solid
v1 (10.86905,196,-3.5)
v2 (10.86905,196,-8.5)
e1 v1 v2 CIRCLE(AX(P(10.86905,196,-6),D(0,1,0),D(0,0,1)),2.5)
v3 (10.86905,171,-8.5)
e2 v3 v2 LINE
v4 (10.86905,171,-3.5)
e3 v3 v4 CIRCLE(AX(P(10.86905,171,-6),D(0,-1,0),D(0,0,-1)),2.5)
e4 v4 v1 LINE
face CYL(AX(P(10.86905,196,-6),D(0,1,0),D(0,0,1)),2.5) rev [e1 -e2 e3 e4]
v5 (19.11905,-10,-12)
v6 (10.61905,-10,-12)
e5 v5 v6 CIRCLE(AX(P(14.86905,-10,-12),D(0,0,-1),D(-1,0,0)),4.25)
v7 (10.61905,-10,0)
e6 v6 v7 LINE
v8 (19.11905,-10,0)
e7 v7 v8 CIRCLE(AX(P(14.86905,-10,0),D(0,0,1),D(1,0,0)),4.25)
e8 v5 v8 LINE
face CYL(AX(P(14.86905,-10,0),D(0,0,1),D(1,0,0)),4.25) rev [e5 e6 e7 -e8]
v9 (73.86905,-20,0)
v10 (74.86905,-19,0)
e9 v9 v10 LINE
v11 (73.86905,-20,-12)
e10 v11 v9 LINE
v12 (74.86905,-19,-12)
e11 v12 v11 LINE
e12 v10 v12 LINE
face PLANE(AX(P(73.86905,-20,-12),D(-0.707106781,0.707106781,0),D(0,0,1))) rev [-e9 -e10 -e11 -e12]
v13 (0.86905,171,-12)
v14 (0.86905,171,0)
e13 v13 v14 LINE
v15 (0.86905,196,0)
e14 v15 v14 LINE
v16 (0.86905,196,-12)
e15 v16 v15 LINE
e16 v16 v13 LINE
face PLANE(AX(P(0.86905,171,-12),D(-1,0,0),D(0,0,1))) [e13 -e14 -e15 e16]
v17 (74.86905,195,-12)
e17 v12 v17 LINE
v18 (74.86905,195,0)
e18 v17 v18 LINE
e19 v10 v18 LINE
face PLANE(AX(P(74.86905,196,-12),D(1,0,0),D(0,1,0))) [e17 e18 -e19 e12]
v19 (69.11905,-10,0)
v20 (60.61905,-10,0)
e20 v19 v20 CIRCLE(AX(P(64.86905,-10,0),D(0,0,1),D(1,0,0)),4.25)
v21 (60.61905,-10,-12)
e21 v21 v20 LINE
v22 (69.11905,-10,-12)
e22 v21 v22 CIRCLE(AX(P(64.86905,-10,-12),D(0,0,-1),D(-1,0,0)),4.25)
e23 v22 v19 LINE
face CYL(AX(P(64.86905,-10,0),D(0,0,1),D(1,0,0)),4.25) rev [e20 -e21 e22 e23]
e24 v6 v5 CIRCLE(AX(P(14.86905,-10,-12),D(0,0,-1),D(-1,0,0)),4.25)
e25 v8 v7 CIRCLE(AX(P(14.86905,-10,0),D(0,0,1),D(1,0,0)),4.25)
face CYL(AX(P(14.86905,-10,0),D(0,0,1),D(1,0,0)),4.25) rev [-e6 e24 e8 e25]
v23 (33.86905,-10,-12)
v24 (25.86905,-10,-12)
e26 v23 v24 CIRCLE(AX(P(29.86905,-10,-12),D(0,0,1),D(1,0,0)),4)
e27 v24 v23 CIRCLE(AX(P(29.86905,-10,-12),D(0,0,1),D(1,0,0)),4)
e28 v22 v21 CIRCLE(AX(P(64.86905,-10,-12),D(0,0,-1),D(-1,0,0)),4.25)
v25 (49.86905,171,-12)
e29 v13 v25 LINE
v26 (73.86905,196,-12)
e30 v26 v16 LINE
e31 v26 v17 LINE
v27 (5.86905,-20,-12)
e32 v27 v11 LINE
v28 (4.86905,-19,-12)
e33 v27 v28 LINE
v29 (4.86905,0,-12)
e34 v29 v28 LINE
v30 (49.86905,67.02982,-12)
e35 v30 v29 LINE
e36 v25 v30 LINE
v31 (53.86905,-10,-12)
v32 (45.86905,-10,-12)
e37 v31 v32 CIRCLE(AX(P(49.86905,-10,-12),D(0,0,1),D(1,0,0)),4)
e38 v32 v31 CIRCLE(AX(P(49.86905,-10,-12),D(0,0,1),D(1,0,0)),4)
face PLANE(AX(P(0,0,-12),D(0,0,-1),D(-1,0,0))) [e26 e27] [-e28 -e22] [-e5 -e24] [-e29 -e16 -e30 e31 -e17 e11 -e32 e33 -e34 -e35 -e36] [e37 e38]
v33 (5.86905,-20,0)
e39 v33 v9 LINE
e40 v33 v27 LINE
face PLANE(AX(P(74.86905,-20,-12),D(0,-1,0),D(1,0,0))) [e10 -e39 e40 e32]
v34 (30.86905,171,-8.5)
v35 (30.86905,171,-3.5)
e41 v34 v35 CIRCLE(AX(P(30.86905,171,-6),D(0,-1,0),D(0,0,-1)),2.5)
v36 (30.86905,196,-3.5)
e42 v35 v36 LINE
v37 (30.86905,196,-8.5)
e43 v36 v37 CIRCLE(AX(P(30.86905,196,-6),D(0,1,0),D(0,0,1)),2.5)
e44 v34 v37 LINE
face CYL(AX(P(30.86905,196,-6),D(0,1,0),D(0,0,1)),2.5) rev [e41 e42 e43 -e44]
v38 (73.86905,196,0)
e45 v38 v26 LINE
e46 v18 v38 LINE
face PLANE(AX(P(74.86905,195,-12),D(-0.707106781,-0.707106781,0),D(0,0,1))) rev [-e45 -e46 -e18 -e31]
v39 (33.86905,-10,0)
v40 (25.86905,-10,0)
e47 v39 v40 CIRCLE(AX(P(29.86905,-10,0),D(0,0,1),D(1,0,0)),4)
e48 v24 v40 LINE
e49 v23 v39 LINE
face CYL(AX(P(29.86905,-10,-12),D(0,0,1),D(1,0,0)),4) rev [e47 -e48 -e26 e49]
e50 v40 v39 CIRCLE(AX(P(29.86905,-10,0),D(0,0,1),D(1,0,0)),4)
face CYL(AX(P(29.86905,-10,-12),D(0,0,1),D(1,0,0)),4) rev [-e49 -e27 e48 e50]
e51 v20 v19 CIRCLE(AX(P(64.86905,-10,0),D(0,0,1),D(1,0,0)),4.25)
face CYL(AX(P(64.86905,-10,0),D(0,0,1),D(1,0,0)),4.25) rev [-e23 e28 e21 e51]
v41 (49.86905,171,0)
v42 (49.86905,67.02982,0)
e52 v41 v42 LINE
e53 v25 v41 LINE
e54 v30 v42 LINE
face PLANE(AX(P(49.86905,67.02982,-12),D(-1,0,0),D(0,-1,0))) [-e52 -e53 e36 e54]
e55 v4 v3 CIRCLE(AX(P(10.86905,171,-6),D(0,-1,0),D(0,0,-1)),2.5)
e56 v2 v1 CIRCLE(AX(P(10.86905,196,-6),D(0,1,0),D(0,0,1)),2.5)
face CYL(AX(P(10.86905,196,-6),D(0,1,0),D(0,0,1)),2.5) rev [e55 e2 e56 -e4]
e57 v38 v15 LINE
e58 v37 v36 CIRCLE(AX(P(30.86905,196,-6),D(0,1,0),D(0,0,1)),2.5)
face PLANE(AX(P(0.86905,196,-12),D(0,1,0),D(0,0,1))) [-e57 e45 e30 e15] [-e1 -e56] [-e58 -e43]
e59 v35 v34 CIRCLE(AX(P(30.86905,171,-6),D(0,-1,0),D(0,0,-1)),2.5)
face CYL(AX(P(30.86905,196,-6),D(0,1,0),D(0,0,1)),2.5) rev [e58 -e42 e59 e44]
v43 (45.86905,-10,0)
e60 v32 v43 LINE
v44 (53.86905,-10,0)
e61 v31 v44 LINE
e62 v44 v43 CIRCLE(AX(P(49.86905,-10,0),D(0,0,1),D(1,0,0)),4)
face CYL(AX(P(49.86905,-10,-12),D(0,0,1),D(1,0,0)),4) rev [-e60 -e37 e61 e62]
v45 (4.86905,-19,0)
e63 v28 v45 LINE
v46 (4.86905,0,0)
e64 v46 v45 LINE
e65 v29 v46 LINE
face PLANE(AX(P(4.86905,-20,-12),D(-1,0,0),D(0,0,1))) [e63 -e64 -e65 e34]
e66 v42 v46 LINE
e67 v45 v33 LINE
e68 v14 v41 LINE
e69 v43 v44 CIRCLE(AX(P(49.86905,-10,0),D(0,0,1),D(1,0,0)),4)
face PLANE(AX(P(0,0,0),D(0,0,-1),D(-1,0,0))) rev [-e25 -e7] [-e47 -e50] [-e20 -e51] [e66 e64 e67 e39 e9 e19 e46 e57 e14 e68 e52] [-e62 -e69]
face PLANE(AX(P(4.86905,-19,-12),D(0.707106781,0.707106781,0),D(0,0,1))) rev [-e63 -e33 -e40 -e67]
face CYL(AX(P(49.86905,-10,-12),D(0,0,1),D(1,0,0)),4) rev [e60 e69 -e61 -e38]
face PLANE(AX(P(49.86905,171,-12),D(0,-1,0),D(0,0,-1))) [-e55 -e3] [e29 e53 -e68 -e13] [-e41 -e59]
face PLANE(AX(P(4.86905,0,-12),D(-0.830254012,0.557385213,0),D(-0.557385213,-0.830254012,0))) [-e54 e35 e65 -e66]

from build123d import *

# Parameters (mm, degrees)
EXTRUDE_1_DEPTH             = 12
HOLE_WIZARD_8_5_8_5_1_D     = 8.5
HOLE_WIZARD_8_5_8_5_1_DEPTH = 15.61
HOLE_WIZARD_8_5_8_5_1_TIP   = 2.453738644
SKETCH_5_R                  = 4
CUT_EXTRUDE_1_DEPTH         = 12
HOLE_WIZARD_M6_1_D          = 5
HOLE_WIZARD_M6_1_DEPTH      = 25
CHAMFER_1_SIZE              = 1
CHAMFER_2_SIZE              = 1


with BuildPart() as part:
    # 草图1 → 凸台-拉伸1 (new body)
    with BuildSketch(Plane.XY):
        Polygon((74.869050236, -20), (4.869050236, -20), (4.869050236, 0), (49.869050236, 67.029820029), (49.869050236, 171), (0.869050236, 171), (0.869050236, 196), (74.869050236, 196), align=None)
    extrude(amount=-EXTRUDE_1_DEPTH)

    # Ø8.5 (8.5) 直径孔1
    with Locations(Plane.XY):
        with Locations((64.869050236, -10), (14.869050236, -10)):
            Hole(HOLE_WIZARD_8_5_8_5_1_D / 2, depth=HOLE_WIZARD_8_5_8_5_1_DEPTH)
            with Locations((0, 0, -(HOLE_WIZARD_8_5_8_5_1_DEPTH + HOLE_WIZARD_8_5_8_5_1_TIP / 2))):  # 120° drill point
                Cone(0, HOLE_WIZARD_8_5_8_5_1_D / 2, HOLE_WIZARD_8_5_8_5_1_TIP, mode=Mode.SUBTRACT)

    # 草图5 → 切除-拉伸1 (cut)
    with BuildSketch(Plane.XY):
        with Locations((29.869050236, -10)):
            Circle(SKETCH_5_R)
        with Locations((49.869050236, -10)):
            Circle(SKETCH_5_R)
    extrude(amount=-CUT_EXTRUDE_1_DEPTH, mode=Mode.SUBTRACT)

    # M6 螺纹孔1
    with Locations(Plane(origin=(0, 196, 0), x_dir=(1, 0, 0), z_dir=(0, 1, 0))):
        with Locations((10.869050236, 6), (30.869050236, 6)):
            Hole(HOLE_WIZARD_M6_1_D / 2, depth=HOLE_WIZARD_M6_1_DEPTH)

    # 倒角1
    chamfer_1_edges = [part.edges().sort_by_distance(p)[0] for p in [
        (74.869050236, -20, -6),
        (74.869050236, 196, -6),
    ]]
    chamfer(chamfer_1_edges, length=CHAMFER_1_SIZE)

    # 倒角2
    chamfer_2_edges = [part.edges().sort_by_distance(p)[0] for p in [
        (4.869050236, -20, -6),
    ]]
    chamfer(chamfer_2_edges, length=CHAMFER_2_SIZE)


solid = part.part
